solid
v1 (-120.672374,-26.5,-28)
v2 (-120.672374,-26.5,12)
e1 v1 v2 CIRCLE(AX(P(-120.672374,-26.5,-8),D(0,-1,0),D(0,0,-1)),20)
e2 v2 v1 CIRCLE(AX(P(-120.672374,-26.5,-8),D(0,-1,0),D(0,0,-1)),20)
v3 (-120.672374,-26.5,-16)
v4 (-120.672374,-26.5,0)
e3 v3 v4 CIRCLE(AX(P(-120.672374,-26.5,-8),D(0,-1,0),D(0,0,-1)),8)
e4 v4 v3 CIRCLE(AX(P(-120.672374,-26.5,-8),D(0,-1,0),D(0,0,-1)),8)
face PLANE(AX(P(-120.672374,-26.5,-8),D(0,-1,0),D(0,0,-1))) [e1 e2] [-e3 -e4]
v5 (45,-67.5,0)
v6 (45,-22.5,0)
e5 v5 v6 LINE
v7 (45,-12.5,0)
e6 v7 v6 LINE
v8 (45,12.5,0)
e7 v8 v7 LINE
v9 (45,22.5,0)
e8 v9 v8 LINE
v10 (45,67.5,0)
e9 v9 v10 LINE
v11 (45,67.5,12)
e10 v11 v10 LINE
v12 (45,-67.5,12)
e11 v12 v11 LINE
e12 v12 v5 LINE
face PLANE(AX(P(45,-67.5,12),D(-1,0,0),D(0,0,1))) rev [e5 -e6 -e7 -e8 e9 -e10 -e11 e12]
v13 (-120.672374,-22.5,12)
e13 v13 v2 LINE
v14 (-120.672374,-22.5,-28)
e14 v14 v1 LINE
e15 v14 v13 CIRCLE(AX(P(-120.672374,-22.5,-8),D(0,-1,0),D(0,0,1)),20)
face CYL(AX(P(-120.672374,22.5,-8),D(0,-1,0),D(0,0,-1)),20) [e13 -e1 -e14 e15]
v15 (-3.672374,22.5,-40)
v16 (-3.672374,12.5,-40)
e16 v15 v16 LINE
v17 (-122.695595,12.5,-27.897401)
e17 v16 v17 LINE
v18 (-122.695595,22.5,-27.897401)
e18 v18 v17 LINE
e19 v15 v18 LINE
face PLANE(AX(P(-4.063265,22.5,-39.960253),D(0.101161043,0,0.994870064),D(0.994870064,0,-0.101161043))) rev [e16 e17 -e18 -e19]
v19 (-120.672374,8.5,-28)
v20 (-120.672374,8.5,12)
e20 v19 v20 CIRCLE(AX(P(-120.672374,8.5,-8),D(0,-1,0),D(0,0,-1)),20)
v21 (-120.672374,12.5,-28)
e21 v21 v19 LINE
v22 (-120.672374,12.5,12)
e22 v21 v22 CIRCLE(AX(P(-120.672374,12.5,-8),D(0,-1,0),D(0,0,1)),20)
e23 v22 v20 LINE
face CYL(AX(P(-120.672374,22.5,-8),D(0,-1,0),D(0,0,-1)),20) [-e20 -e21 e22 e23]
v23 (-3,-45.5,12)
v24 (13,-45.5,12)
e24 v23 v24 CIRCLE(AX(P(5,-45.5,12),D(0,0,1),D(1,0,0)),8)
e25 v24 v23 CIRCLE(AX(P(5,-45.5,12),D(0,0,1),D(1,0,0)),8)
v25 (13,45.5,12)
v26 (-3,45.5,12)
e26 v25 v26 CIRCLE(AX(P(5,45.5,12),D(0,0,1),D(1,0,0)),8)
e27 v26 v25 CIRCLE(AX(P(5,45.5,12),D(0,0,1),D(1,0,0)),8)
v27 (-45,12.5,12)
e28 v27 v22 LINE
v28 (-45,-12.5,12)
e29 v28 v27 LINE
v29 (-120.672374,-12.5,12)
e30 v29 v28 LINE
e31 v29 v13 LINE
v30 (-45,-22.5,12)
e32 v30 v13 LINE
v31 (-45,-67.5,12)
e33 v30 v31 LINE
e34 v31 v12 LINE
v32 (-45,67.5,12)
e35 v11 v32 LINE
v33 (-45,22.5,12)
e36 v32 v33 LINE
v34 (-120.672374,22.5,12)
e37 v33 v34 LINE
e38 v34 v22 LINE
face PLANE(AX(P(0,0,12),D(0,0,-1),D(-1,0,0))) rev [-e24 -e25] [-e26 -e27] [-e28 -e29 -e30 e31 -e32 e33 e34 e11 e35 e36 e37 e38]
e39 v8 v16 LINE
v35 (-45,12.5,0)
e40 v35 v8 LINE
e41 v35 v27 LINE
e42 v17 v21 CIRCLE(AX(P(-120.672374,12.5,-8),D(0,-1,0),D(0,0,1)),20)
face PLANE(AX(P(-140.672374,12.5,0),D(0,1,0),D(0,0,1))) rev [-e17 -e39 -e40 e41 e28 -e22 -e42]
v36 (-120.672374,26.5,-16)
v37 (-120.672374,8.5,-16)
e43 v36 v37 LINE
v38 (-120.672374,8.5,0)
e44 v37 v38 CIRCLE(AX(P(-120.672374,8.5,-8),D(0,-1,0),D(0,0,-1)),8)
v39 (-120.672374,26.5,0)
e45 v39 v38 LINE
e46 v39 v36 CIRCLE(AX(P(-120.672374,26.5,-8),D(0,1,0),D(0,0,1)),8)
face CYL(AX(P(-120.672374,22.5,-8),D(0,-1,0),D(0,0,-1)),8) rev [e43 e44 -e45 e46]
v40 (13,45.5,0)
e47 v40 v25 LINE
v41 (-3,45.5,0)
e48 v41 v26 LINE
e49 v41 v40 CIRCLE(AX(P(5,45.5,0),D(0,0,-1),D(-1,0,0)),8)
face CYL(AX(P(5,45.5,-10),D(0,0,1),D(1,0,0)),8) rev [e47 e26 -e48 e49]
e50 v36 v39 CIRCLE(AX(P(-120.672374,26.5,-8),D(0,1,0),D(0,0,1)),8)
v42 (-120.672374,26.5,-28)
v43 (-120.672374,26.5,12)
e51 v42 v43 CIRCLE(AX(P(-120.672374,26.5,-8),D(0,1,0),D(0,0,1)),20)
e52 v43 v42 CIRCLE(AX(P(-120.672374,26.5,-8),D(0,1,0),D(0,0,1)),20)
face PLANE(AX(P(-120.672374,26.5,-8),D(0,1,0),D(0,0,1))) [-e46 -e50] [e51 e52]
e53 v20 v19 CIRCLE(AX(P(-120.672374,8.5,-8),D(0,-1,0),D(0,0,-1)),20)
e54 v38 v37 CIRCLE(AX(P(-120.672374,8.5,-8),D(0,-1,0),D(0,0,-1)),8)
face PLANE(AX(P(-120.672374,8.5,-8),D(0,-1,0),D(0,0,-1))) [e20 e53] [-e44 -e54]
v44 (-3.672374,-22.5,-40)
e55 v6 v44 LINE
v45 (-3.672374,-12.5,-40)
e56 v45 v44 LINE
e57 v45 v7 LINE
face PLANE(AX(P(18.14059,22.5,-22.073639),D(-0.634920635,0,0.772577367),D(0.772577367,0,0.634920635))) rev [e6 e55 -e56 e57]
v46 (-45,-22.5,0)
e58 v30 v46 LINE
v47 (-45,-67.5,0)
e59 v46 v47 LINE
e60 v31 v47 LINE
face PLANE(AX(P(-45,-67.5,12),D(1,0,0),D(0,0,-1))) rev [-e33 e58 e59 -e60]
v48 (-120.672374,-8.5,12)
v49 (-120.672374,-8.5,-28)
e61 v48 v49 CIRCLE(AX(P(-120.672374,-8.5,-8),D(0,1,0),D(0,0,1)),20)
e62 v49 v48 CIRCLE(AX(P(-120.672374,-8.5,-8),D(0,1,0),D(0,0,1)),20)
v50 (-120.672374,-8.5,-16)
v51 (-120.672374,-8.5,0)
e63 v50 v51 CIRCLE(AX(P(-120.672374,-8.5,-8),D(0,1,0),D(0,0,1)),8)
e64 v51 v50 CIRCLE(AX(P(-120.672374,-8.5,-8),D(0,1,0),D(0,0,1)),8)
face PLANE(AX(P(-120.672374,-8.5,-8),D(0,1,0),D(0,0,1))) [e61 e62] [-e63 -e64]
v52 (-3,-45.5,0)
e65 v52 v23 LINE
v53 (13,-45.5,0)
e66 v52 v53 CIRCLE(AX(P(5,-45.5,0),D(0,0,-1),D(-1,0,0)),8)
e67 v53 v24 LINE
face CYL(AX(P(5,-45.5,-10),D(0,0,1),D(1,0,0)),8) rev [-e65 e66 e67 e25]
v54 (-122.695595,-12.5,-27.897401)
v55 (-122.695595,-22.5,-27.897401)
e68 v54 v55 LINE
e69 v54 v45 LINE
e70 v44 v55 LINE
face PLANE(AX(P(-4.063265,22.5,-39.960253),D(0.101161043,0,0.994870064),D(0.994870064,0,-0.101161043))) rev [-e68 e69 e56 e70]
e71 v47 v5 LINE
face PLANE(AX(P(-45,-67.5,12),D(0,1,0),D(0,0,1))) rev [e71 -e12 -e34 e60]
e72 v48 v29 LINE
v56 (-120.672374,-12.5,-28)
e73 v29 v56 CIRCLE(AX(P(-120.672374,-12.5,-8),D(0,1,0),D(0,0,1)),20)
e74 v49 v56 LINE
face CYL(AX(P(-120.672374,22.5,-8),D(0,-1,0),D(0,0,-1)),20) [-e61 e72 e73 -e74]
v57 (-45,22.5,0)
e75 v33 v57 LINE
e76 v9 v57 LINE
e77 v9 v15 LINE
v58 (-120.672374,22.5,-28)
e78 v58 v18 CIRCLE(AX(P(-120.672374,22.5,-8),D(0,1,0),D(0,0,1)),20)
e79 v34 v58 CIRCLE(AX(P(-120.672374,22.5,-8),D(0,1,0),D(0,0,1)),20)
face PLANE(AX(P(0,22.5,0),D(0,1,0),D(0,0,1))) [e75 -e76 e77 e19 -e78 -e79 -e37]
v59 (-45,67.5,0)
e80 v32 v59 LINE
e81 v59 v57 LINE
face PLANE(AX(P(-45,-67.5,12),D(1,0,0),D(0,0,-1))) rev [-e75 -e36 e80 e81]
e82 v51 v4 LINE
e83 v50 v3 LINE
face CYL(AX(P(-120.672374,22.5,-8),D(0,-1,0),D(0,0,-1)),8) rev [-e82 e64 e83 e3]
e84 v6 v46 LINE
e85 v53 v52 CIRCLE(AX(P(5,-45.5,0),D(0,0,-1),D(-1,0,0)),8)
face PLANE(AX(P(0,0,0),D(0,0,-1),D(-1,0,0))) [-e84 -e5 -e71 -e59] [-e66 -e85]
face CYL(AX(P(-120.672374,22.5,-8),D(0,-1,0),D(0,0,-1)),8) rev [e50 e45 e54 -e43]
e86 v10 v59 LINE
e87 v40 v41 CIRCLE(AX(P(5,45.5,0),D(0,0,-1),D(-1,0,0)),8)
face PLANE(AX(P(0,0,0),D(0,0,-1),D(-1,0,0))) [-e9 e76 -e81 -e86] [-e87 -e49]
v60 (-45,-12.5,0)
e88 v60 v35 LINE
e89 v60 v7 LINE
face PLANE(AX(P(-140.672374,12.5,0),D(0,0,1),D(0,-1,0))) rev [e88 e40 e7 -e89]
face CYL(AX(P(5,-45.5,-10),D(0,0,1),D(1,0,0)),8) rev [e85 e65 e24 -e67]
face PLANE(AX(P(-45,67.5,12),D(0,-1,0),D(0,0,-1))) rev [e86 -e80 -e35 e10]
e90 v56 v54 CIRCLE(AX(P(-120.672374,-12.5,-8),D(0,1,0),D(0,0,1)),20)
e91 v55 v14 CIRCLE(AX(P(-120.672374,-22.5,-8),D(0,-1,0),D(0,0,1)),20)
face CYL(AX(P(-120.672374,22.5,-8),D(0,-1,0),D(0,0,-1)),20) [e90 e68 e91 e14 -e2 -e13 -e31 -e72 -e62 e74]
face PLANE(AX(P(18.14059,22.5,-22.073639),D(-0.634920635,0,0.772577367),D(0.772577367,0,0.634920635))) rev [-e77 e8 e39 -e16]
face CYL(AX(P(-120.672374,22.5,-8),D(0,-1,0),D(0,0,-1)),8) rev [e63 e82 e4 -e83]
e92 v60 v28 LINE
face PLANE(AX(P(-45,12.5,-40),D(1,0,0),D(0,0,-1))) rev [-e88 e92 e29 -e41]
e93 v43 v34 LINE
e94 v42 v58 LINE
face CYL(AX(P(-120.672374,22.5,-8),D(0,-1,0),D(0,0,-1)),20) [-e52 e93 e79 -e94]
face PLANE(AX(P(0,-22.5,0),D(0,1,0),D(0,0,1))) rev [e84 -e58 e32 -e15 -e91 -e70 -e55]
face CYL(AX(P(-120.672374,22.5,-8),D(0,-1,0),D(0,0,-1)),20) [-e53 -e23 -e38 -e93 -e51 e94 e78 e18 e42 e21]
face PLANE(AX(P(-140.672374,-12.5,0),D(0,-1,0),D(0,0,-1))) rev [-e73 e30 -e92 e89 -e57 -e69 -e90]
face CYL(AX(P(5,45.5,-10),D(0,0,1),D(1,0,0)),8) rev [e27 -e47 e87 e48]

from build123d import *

# Parameters (mm, degrees)
BASE_PLATE_SKETCH_W        = 90
BASE_PLATE_SKETCH_H        = 135
BASE_PLATE_DEPTH           = 12
MOUNTING_HOLES_SKETCH_R    = 8
MOUNTING_HOLES_2X_16_DEPTH = 22
CLEVIS_ARM_SKETCH_R        = 20
CLEVIS_ARM_SKETCH_R_2      = 8
CLEVIS_ARM_DEPTH           = 22.5
CLEVIS_SLOT_DEPTH          = 162.074413963
CLEVIS_SLOT_DEPTH_BACK     = 162.074413963
CLEVIS_SLOT_SKETCH_W       = 40
CLEVIS_SLOT_SKETCH_H       = 25
PIN_HOLE_DEPTH             = 165.465701085
PIN_HOLE_DEPTH_BACK        = 165.465701085
PIN_HOLE_SKETCH_W          = 94.002676874
PIN_HOLE_SKETCH_H          = 25
LUG_BOSS_1_SKETCH_R        = 20
LUG_BOSS_1_SKETCH_R_2      = 8
LUG_BOSS_1_40_DEPTH        = 4
LUG_START                  = 4
LUG_BOSS_2_SKETCH_R        = 20
LUG_BOSS_2_SKETCH_R_2      = 8
LUG_BOSS_2_40_DEPTH        = 4
LUG_BOSS_3_SKETCH_R        = 20
LUG_BOSS_3_SKETCH_R_2      = 8
LUG_BOSS_3_40_DEPTH        = 4
LUG_BOSS_4_SKETCH_R        = 20
LUG_BOSS_4_SKETCH_R_2      = 8
LUG_BOSS_4_40_DEPTH        = 4


with BuildPart() as part:
    # Base Plate Sketch → Base Plate (new body)
    with BuildSketch(Plane.XY):
        Rectangle(BASE_PLATE_SKETCH_W, BASE_PLATE_SKETCH_H)
    extrude(amount=BASE_PLATE_DEPTH)

    # Mounting Holes Sketch → Mounting Holes 2xØ16 (cut)
    with BuildSketch(Plane.XY.offset(12)):
        with Locations((5, -45.5)):
            Circle(MOUNTING_HOLES_SKETCH_R)
        with Locations((5, 45.5)):
            Circle(MOUNTING_HOLES_SKETCH_R)
    extrude(amount=-MOUNTING_HOLES_2X_16_DEPTH, mode=Mode.SUBTRACT)

    # Clevis Arm Sketch → Clevis Arm (add, symmetric)
    # profile 1 of 2: a face of its own
    with BuildSketch(Plane(origin=(0, 0, 0), x_dir=(1, 0, 0), z_dir=(0, 1, 0))):
        with BuildLine():
            Line((-120.672374095, -12), (-45, -12))
            Line((-45, -12), (-45, 0))
            Line((-45, 0), (45, 0))
            Line((45, 0), (-3.672374095, 40))
            Line((-3.672374095, 40), (-122.695594955, 27.897401271))
            ThreePointArc((-122.695594955, 27.897401271), (-107.264622926, 22.84022266), (-100.672374095, 8))
            ThreePointArc((-100.672374095, 8), (-106.530238471, -6.142135624), (-120.672374095, -12))
        make_face()
    # profile 2 of 2: a face of its own
    with BuildSketch(Plane(origin=(0, 0, 0), x_dir=(1, 0, 0), z_dir=(0, 1, 0))):
        with Locations((-120.672374095, 8)):
            Circle(CLEVIS_ARM_SKETCH_R)
        with Locations(Location((-120.672374095, 8, 0), (0, 0, 90))):
            Circle(CLEVIS_ARM_SKETCH_R_2, mode=Mode.SUBTRACT)
    extrude(amount=CLEVIS_ARM_DEPTH, both=True)

    # Clevis Slot Sketch → Clevis Slot (cut, two sides: drawn at the far end of the back side and taken through both)
    with BuildSketch(Plane(origin=(0, 0, 0), x_dir=(0, 0, -1), z_dir=(1, 0, 0)).offset(-CLEVIS_SLOT_DEPTH_BACK)):
        with Locations((20, 0)):
            Rectangle(CLEVIS_SLOT_SKETCH_W, CLEVIS_SLOT_SKETCH_H)
    extrude(amount=CLEVIS_SLOT_DEPTH + CLEVIS_SLOT_DEPTH_BACK, mode=Mode.SUBTRACT)

    # Pin Hole Sketch → Pin Hole (cut, two sides: drawn at the far end of the back side and taken through both)
    with BuildSketch(Plane.XY.offset(12).offset(-PIN_HOLE_DEPTH_BACK)):
        with Locations((-92.001338437, 0)):
            Rectangle(PIN_HOLE_SKETCH_W, PIN_HOLE_SKETCH_H)
    extrude(amount=PIN_HOLE_DEPTH + PIN_HOLE_DEPTH_BACK, mode=Mode.SUBTRACT)

    # Lug Boss 1 Sketch → Lug Boss 1 Ø40 (add)
    with BuildSketch(Plane.XZ.offset(22.5)):
        with Locations(Location((-120.672374095, -8, 0), (0, 0, 270))):
            Circle(LUG_BOSS_1_SKETCH_R)
        with Locations(Location((-120.672374095, -8, 0), (0, 0, 270))):
            Circle(LUG_BOSS_1_SKETCH_R_2, mode=Mode.SUBTRACT)
    extrude(amount=LUG_BOSS_1_40_DEPTH)

    # Lug Boss 2 Sketch → Lug Boss 2 Ø40 (add)
    with BuildSketch(Plane(origin=(0, -12.5, 0), x_dir=(1, 0, 0), z_dir=(0, 1, 0)).offset(LUG_START)):
        with Locations(Location((-120.672374095, 8, 0), (0, 0, 90))):
            Circle(LUG_BOSS_2_SKETCH_R)
        with Locations(Location((-120.672374095, 8, 0), (0, 0, 90))):
            Circle(LUG_BOSS_2_SKETCH_R_2, mode=Mode.SUBTRACT)
    extrude(amount=-LUG_BOSS_2_40_DEPTH)

    # Lug Boss 3 Sketch → Lug Boss 3 Ø40 (add)
    with BuildSketch(Plane(origin=(0, 22.5, 0), x_dir=(1, 0, 0), z_dir=(0, 1, 0)).offset(LUG_START)):
        with Locations(Location((-120.672374095, 8, 0), (0, 0, 270))):
            Circle(LUG_BOSS_3_SKETCH_R)
        with Locations(Location((-120.672374095, 8, 0), (0, 0, 90))):
            Circle(LUG_BOSS_3_SKETCH_R_2, mode=Mode.SUBTRACT)
    extrude(amount=-LUG_BOSS_3_40_DEPTH)

    # Lug Boss 4 Sketch → Lug Boss 4 Ø40 (add)
    with BuildSketch(Plane.XZ.offset(-12.5)):
        with Locations(Location((-120.672374095, -8, 0), (0, 0, 270))):
            Circle(LUG_BOSS_4_SKETCH_R)
        with Locations(Location((-120.672374095, -8, 0), (0, 0, 270))):
            Circle(LUG_BOSS_4_SKETCH_R_2, mode=Mode.SUBTRACT)
    extrude(amount=LUG_BOSS_4_40_DEPTH)


solid = part.part
